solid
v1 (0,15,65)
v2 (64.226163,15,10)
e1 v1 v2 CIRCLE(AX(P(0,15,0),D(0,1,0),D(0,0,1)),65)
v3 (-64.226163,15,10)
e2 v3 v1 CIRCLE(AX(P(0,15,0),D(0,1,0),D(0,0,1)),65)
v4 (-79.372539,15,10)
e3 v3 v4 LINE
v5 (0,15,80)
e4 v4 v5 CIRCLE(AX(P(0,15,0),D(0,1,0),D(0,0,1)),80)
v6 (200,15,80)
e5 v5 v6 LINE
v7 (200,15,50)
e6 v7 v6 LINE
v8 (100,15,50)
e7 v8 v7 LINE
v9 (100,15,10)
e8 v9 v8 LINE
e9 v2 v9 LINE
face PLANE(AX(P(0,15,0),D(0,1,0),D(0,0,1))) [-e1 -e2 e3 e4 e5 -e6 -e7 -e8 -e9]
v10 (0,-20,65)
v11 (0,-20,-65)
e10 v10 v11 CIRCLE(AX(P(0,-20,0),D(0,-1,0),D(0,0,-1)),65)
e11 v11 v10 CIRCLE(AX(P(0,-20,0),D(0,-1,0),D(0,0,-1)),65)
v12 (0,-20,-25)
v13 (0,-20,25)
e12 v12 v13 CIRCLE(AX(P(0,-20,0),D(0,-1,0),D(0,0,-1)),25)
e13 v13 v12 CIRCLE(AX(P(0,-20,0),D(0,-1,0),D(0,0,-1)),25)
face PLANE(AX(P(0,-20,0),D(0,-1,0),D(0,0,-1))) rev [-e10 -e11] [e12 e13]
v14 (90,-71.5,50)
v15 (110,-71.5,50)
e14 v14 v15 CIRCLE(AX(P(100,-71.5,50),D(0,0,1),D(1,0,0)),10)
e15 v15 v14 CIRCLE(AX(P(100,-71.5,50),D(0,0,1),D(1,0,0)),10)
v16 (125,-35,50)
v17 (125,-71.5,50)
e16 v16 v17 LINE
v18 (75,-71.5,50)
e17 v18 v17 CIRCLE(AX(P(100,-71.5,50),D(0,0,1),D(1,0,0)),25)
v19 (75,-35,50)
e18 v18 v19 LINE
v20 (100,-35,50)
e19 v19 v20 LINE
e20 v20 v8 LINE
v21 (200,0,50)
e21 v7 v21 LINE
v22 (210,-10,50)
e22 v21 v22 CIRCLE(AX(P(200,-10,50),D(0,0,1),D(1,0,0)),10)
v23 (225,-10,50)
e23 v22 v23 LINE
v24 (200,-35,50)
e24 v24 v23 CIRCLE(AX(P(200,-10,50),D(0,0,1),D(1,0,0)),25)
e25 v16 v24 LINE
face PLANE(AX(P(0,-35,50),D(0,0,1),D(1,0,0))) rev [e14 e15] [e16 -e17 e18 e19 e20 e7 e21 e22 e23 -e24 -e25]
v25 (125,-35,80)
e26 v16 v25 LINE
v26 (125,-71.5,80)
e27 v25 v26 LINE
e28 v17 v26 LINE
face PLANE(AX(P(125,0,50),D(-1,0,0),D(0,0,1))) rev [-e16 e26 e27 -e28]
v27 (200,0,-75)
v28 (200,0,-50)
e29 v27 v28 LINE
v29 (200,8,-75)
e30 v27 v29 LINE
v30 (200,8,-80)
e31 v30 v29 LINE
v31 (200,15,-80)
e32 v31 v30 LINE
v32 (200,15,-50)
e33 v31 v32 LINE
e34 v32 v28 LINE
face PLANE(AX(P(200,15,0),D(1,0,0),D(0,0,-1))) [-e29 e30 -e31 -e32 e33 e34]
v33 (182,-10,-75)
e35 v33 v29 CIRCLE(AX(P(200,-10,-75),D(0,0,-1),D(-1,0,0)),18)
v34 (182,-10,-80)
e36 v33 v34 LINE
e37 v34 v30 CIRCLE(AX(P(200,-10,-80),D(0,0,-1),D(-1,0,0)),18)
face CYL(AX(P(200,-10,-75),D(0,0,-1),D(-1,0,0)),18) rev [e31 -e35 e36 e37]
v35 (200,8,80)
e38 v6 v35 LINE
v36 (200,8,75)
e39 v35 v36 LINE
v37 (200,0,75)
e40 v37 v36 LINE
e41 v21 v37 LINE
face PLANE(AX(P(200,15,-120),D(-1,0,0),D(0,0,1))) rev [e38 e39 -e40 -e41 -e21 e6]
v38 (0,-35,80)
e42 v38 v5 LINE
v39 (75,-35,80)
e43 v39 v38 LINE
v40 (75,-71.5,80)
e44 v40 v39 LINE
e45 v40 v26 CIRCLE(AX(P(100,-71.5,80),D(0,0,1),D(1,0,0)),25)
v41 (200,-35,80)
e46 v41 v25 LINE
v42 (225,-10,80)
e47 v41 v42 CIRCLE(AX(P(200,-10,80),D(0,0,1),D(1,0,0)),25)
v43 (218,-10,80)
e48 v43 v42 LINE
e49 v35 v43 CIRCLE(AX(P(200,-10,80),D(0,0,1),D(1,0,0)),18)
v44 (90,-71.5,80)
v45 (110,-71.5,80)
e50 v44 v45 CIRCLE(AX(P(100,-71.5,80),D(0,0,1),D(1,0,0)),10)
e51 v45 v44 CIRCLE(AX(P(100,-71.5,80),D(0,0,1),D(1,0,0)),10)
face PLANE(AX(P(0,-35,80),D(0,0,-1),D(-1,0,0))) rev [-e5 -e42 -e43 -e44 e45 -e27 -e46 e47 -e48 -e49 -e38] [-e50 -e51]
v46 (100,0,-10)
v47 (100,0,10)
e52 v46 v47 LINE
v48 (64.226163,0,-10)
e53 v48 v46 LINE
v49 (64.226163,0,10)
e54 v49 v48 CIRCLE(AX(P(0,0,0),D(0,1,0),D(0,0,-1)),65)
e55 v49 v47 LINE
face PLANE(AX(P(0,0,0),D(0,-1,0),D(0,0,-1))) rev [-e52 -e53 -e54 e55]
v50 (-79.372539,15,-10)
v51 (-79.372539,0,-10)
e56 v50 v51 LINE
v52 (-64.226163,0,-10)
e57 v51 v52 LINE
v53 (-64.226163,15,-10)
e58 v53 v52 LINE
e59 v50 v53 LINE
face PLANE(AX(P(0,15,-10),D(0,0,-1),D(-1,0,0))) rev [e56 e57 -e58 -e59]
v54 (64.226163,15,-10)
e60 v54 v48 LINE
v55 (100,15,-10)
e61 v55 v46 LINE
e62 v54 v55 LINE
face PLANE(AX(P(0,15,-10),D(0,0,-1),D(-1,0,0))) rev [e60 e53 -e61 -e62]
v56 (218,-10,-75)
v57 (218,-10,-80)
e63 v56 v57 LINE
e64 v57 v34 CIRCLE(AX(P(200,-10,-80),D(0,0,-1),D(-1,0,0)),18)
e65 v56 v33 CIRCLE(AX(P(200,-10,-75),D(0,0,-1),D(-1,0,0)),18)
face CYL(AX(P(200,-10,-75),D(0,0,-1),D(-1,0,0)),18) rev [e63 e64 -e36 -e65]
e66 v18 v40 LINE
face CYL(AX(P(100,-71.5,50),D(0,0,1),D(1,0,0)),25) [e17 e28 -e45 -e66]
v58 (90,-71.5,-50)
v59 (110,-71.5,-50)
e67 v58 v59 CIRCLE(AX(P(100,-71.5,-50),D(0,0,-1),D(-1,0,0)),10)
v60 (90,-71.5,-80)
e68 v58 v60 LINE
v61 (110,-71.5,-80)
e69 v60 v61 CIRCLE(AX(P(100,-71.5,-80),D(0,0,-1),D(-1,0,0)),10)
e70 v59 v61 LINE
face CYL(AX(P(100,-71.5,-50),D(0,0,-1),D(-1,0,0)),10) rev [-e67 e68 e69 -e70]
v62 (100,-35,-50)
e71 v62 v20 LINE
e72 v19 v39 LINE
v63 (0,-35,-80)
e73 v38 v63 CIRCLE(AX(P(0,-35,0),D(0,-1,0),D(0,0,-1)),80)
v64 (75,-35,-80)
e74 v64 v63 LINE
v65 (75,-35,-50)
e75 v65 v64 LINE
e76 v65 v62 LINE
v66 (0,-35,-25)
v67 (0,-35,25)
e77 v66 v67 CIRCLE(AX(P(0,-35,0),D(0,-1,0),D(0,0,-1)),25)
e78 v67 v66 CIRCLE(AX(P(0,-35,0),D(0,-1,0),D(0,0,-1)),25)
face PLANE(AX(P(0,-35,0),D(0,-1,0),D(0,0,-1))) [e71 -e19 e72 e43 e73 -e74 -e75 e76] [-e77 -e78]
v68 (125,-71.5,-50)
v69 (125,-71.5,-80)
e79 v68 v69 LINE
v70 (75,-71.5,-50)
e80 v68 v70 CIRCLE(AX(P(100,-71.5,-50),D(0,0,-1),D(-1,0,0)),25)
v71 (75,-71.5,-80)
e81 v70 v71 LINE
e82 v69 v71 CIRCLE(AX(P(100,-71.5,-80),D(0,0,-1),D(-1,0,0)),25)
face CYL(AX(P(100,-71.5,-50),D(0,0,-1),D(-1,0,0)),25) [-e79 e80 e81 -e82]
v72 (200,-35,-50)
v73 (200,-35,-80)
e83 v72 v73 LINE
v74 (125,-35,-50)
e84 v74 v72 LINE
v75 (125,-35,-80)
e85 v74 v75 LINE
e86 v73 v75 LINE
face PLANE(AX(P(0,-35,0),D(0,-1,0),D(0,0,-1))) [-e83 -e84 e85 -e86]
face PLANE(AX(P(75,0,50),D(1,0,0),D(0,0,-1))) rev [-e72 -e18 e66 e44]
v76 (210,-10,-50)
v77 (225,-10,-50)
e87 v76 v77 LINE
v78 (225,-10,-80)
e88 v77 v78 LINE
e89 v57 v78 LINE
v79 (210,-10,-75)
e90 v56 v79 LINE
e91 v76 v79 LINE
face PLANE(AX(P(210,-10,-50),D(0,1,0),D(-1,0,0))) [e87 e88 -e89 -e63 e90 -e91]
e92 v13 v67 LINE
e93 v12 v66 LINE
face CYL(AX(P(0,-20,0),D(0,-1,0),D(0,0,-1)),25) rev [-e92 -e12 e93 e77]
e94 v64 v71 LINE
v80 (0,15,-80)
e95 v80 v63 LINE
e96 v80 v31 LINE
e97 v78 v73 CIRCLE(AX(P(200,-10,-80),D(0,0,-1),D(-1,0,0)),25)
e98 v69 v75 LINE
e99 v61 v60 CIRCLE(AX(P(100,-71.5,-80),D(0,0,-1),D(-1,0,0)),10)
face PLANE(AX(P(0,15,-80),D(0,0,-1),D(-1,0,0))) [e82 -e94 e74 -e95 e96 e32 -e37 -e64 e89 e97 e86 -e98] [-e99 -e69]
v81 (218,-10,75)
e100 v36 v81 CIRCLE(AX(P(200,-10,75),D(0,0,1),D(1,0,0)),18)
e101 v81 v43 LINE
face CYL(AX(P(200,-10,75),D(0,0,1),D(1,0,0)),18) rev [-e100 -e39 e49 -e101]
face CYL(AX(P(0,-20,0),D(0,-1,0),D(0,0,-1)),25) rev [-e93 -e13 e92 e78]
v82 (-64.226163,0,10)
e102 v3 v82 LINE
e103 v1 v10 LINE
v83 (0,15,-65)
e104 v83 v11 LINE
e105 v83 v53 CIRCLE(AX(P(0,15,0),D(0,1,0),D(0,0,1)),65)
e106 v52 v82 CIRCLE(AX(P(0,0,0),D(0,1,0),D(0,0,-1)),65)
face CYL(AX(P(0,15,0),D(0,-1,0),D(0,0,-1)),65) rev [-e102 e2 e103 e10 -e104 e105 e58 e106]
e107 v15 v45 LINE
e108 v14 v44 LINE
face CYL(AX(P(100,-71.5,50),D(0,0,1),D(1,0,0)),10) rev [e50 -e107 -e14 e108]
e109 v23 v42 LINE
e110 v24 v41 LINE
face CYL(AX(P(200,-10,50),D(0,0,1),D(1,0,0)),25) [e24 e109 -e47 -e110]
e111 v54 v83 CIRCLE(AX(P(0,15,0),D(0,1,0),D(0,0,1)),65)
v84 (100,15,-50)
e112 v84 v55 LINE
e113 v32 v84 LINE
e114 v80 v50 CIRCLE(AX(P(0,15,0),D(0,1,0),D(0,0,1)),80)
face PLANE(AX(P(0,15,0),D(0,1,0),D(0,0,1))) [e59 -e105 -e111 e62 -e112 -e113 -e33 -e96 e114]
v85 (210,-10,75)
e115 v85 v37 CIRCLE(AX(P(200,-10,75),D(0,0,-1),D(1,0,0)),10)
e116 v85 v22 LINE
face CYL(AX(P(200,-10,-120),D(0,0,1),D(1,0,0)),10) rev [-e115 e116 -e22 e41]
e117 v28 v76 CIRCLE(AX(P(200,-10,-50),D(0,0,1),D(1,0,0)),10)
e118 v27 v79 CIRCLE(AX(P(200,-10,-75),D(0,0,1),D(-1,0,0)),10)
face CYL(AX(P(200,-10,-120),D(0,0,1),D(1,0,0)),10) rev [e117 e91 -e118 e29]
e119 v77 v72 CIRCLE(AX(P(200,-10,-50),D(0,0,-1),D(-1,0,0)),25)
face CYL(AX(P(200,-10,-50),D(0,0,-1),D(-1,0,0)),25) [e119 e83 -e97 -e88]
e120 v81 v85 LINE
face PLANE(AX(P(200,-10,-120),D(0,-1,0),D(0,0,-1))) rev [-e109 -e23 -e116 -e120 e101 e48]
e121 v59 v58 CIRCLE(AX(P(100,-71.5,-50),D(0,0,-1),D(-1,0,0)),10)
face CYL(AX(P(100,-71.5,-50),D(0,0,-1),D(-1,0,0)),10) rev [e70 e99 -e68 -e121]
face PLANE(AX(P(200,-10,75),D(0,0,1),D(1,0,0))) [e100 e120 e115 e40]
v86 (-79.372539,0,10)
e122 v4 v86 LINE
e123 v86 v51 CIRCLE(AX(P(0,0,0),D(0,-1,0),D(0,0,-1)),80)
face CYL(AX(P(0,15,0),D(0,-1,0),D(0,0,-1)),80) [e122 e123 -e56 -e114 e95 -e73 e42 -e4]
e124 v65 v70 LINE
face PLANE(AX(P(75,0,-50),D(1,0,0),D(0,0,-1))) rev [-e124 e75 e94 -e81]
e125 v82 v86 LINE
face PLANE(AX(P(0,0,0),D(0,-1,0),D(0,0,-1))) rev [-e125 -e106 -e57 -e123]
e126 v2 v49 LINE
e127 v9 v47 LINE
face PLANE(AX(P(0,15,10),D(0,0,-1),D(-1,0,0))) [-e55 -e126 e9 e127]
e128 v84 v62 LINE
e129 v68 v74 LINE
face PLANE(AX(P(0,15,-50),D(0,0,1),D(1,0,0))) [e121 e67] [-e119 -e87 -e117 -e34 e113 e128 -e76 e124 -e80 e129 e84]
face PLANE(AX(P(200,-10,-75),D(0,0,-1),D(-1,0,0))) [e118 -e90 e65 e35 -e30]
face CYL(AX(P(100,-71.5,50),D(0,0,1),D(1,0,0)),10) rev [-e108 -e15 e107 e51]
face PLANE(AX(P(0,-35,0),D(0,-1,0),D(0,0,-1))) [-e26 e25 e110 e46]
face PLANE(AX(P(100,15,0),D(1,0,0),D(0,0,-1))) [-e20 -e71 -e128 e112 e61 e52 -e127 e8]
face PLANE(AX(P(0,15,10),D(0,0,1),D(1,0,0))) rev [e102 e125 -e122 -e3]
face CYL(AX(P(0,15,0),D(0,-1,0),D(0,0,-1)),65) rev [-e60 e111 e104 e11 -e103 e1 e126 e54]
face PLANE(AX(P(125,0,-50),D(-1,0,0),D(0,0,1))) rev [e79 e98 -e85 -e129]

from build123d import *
from build123d.topology import SkipClean

# Parameters (mm, degrees)
BASE_PLATE_DEPTH                = 15
CIRCULAR_START                  = 35
CIRCULAR_HOUSING_DEPTH          = 35
HOUSING_EXTENSION_SKETCH_R      = 65
HOUSING_EXTENSION_SKETCH_R_2    = 25
HOUSING_EXTENSION_DEPTH         = 15
CLEVIS_LUG_BLOCK_SKETCH_R       = 25
CLEVIS_LUG_BLOCK_SKETCH_R_2     = 10
CLEVIS_LUG_BLOCK_DEPTH          = 30
CLEVIS_START                    = -30
CLEVIS_LUG_EXTENSION_SKETCH_R   = 25
CLEVIS_LUG_EXTENSION_SKETCH_R_2 = 10
CLEVIS_LUG_EXTENSION_DEPTH      = 30
PIVOT_LUG_SKETCH_R              = 25
PIVOT_LUGS_DEPTH                = 30
PIVOT_PIN_HOLE_SKETCH_R         = 10
PIVOT_PIN_HOLE_20_DEPTH         = 200
CLEVIS_SLOT_25_DEPTH            = 200
SPOT_FACE_A_SKETCH_R            = 18
SPOT_FACE_A_36X5_DEPTH          = 5
LUG_START                       = -30
LUG_FILL_BOSS_DEPTH             = 30
SPOT_START                      = -5
SPOT_FACE_B_SKETCH_R            = 18
SPOT_FACE_B_36X5_DEPTH          = 5


with BuildPart() as part:
    # Base Plate Sketch → Base Plate (new body)
    with BuildSketch(Plane(origin=(0, 0, 0), x_dir=(1, 0, 0), z_dir=(0, 1, 0))):
        with BuildLine():
            ThreePointArc((64.226162893, -10), (0, -65), (-64.226162893, -10))
            Line((-64.226162893, -10), (-79.372539332, -10))
            ThreePointArc((-79.372539332, -10), (-52.915026221, -60), (0, -80))
            ThreePointArc((0, -80), (52.915026221, -60), (79.372539332, -10))
            Line((79.372539332, -10), (64.226162893, -10))
        make_face()
        with BuildLine():
            ThreePointArc((0, 80), (-52.915026221, 60), (-79.372539332, 10))
            Line((-79.372539332, 10), (-64.226162893, 10))
            ThreePointArc((-64.226162893, 10), (0, 65), (64.226162893, 10))
            Line((64.226162893, 10), (79.372539332, 10))
            ThreePointArc((79.372539332, 10), (52.915026221, 60), (0, 80))
        make_face()
        with BuildLine():
            Line((200, 80), (0, 80))
            ThreePointArc((0, 80), (52.915026221, 60), (79.372539332, 10))
            Line((79.372539332, 10), (100, 10))
            Line((100, 10), (100, 50))
            Line((100, 50), (200, 50))
            Line((200, 50), (200, 80))
        make_face()
        with BuildLine():
            ThreePointArc((79.372539332, -10), (52.915026221, -60), (0, -80))
            Line((0, -80), (200, -80))
            Line((200, -80), (200, -50))
            Line((200, -50), (100, -50))
            Line((100, -50), (100, -10))
            Line((100, -10), (79.372539332, -10))
        make_face()
    extrude(amount=BASE_PLATE_DEPTH)

    # Circular Housing Sketch → Circular Housing (add)
    with BuildSketch(Plane.XZ.offset(CIRCULAR_START)):
        with BuildLine():
            ThreePointArc((79.372539332, 10), (52.915026221, 60), (0, 80))
            ThreePointArc((0, 80), (-52.915026221, 60), (-79.372539332, 10))
            Line((-79.372539332, 10), (-64.226162893, 10))
            ThreePointArc((-64.226162893, 10), (0, 65), (64.226162893, 10))
            Line((64.226162893, 10), (79.372539332, 10))
        make_face()
        with BuildLine():
            Line((-64.226162893, 10), (-79.372539332, 10))
            ThreePointArc((-79.372539332, 10), (-60, -52.915026221), (0, -80))
            ThreePointArc((0, -80), (56.568542495, -56.568542495), (80, 0))
            ThreePointArc((80, 0), (79.842980739, 5.009833003), (79.372539332, 10))
            Line((79.372539332, 10), (64.226162893, 10))
            ThreePointArc((64.226162893, 10), (64.806251967, 5.014948252), (65, 0))
            ThreePointArc((65, 0), (-5.014948252, -64.806251967), (-64.226162893, 10))
        make_face()
        with BuildLine():
            Line((200, 80), (0, 80))
            ThreePointArc((0, 80), (52.915026221, 60), (79.372539332, 10))
            Line((79.372539332, 10), (100, 10))
            Line((100, 10), (100, 50))
            Line((100, 50), (200, 50))
            Line((200, 50), (200, 80))
        make_face()
        with BuildLine():
            Line((100, 10), (79.372539332, 10))
            ThreePointArc((79.372539332, 10), (79.842980739, 5.009833003), (80, 0))
            ThreePointArc((80, 0), (56.568542495, -56.568542495), (0, -80))
            Line((0, -80), (200, -80))
            Line((200, -80), (200, -50))
            Line((200, -50), (100, -50))
            Line((100, -50), (100, 10))
        make_face()
    extrude(amount=-CIRCULAR_HOUSING_DEPTH)

    # Housing Extension Sketch → Housing Extension (add)
    with BuildSketch(Plane.XZ.offset(35)):
        with Locations(Location((0, 0, 0), (0, 0, 270))):
            Circle(HOUSING_EXTENSION_SKETCH_R)
        with Locations(Location((0, 0, 0), (0, 0, 270))):
            Circle(HOUSING_EXTENSION_SKETCH_R_2, mode=Mode.SUBTRACT)
    extrude(amount=-HOUSING_EXTENSION_DEPTH)

    # Clevis Lug Block Sketch → Clevis Lug Block (add)
    # profile 1 of 2: a face of its own
    with SkipClean():  # the faces are left unmerged after this step: merging them gives an invalid solid
        with BuildSketch(Plane.XY.offset(80)):
            with BuildLine():
                Line((75, -35), (75, -71.5))
                ThreePointArc((75, -71.5), (100, -46.5), (125, -71.5))
                Line((125, -71.5), (125, -35))
                Line((125, -35), (75, -35))
            make_face()
        # profile 2 of 2: a face of its own
        with BuildSketch(Plane.XY.offset(80)):
            with Locations((100, -71.5)):
                Circle(CLEVIS_LUG_BLOCK_SKETCH_R)
            with Locations((100, -71.5)):
                Circle(CLEVIS_LUG_BLOCK_SKETCH_R_2, mode=Mode.SUBTRACT)
        extrude(amount=-CLEVIS_LUG_BLOCK_DEPTH)

    # Clevis Lug Extension Sketch → Clevis Lug Extension (add)
    # profile 1 of 2: a face of its own
    with SkipClean():  # the faces are left unmerged after this step: merging them gives an invalid solid
        with BuildSketch(Plane(origin=(0, 0, -80), x_dir=(-1, 0, 0), z_dir=(0, 0, -1)).offset(CLEVIS_START)):
            with BuildLine():
                Line((-125, -35), (-125, -71.5))
                ThreePointArc((-125, -71.5), (-100, -46.5), (-75, -71.5))
                Line((-75, -71.5), (-75, -35))
                Line((-75, -35), (-125, -35))
            make_face()
        # profile 2 of 2: a face of its own
        with BuildSketch(Plane(origin=(0, 0, -80), x_dir=(-1, 0, 0), z_dir=(0, 0, -1)).offset(CLEVIS_START)):
            with Locations((-100, -71.5)):
                Circle(CLEVIS_LUG_EXTENSION_SKETCH_R)
            with Locations(Location((-100, -71.5, 0), (0, 0, 180))):
                Circle(CLEVIS_LUG_EXTENSION_SKETCH_R_2, mode=Mode.SUBTRACT)
        extrude(amount=CLEVIS_LUG_EXTENSION_DEPTH)

    # Pivot Lug Sketch → Pivot Lugs (add)
    with SkipClean():  # the faces are left unmerged after this step: merging them gives an invalid solid
        with BuildSketch(Plane.XY.offset(80)):
            with Locations((200, -10)):
                Circle(PIVOT_LUG_SKETCH_R)
        extrude(amount=-PIVOT_LUGS_DEPTH)

    # Pivot Pin Hole Sketch → Pivot Pin Hole Ø20 (cut)
    with SkipClean():  # the faces are left unmerged after this step: merging them gives an invalid solid
        with BuildSketch(Plane.XY.offset(80)):
            with Locations((200, -10)):
                Circle(PIVOT_PIN_HOLE_SKETCH_R)
        extrude(amount=-PIVOT_PIN_HOLE_20_DEPTH, mode=Mode.SUBTRACT)

    # Clevis Slot Sketch → Clevis Slot 25 (cut)
    with SkipClean():  # the faces are left unmerged after this step: merging them gives an invalid solid
        with BuildSketch(Plane.XY.offset(80)):
            with BuildLine():
                Line((200, 15), (200, -10))
                Line((200, -10), (225, -10))
                ThreePointArc((225, -10), (217.67766953, 7.67766953), (200, 15))
            make_face()
        extrude(amount=-CLEVIS_SLOT_25_DEPTH, mode=Mode.SUBTRACT)

    # Spot Face A Sketch → Spot Face A Ø36x5 (cut)
    with SkipClean():  # the faces are left unmerged after this step: merging them gives an invalid solid
        with BuildSketch(Plane.XY.offset(80)):
            with Locations((200, -10)):
                Circle(SPOT_FACE_A_SKETCH_R)
        extrude(amount=-SPOT_FACE_A_36X5_DEPTH, mode=Mode.SUBTRACT)

    # Lug Fill Sketch → Lug Fill Boss (add)
    with SkipClean():  # the faces are left unmerged after this step: merging them gives an invalid solid
        with BuildSketch(Plane(origin=(0, 0, -80), x_dir=(-1, 0, 0), z_dir=(0, 0, -1)).offset(LUG_START)):
            with BuildLine():
                Line((-210, -10), (-225, -10))
                ThreePointArc((-225, -10), (-217.67766953, -27.67766953), (-200, -35))
                Line((-200, -35), (-200, -20))
                ThreePointArc((-200, -20), (-207.071067812, -17.071067812), (-210, -10))
            make_face()
        extrude(amount=LUG_FILL_BOSS_DEPTH)

    # Spot Face B Sketch → Spot Face B Ø36x5 (cut)
    with SkipClean():  # the faces are left unmerged after this step: merging them gives an invalid solid
        with BuildSketch(Plane(origin=(0, 0, -80), x_dir=(-1, 0, 0), z_dir=(0, 0, -1)).offset(SPOT_START)):
            with Locations((-200, -10)):
                Circle(SPOT_FACE_B_SKETCH_R)
        extrude(amount=SPOT_FACE_B_36X5_DEPTH, mode=Mode.SUBTRACT)


solid = part.part
